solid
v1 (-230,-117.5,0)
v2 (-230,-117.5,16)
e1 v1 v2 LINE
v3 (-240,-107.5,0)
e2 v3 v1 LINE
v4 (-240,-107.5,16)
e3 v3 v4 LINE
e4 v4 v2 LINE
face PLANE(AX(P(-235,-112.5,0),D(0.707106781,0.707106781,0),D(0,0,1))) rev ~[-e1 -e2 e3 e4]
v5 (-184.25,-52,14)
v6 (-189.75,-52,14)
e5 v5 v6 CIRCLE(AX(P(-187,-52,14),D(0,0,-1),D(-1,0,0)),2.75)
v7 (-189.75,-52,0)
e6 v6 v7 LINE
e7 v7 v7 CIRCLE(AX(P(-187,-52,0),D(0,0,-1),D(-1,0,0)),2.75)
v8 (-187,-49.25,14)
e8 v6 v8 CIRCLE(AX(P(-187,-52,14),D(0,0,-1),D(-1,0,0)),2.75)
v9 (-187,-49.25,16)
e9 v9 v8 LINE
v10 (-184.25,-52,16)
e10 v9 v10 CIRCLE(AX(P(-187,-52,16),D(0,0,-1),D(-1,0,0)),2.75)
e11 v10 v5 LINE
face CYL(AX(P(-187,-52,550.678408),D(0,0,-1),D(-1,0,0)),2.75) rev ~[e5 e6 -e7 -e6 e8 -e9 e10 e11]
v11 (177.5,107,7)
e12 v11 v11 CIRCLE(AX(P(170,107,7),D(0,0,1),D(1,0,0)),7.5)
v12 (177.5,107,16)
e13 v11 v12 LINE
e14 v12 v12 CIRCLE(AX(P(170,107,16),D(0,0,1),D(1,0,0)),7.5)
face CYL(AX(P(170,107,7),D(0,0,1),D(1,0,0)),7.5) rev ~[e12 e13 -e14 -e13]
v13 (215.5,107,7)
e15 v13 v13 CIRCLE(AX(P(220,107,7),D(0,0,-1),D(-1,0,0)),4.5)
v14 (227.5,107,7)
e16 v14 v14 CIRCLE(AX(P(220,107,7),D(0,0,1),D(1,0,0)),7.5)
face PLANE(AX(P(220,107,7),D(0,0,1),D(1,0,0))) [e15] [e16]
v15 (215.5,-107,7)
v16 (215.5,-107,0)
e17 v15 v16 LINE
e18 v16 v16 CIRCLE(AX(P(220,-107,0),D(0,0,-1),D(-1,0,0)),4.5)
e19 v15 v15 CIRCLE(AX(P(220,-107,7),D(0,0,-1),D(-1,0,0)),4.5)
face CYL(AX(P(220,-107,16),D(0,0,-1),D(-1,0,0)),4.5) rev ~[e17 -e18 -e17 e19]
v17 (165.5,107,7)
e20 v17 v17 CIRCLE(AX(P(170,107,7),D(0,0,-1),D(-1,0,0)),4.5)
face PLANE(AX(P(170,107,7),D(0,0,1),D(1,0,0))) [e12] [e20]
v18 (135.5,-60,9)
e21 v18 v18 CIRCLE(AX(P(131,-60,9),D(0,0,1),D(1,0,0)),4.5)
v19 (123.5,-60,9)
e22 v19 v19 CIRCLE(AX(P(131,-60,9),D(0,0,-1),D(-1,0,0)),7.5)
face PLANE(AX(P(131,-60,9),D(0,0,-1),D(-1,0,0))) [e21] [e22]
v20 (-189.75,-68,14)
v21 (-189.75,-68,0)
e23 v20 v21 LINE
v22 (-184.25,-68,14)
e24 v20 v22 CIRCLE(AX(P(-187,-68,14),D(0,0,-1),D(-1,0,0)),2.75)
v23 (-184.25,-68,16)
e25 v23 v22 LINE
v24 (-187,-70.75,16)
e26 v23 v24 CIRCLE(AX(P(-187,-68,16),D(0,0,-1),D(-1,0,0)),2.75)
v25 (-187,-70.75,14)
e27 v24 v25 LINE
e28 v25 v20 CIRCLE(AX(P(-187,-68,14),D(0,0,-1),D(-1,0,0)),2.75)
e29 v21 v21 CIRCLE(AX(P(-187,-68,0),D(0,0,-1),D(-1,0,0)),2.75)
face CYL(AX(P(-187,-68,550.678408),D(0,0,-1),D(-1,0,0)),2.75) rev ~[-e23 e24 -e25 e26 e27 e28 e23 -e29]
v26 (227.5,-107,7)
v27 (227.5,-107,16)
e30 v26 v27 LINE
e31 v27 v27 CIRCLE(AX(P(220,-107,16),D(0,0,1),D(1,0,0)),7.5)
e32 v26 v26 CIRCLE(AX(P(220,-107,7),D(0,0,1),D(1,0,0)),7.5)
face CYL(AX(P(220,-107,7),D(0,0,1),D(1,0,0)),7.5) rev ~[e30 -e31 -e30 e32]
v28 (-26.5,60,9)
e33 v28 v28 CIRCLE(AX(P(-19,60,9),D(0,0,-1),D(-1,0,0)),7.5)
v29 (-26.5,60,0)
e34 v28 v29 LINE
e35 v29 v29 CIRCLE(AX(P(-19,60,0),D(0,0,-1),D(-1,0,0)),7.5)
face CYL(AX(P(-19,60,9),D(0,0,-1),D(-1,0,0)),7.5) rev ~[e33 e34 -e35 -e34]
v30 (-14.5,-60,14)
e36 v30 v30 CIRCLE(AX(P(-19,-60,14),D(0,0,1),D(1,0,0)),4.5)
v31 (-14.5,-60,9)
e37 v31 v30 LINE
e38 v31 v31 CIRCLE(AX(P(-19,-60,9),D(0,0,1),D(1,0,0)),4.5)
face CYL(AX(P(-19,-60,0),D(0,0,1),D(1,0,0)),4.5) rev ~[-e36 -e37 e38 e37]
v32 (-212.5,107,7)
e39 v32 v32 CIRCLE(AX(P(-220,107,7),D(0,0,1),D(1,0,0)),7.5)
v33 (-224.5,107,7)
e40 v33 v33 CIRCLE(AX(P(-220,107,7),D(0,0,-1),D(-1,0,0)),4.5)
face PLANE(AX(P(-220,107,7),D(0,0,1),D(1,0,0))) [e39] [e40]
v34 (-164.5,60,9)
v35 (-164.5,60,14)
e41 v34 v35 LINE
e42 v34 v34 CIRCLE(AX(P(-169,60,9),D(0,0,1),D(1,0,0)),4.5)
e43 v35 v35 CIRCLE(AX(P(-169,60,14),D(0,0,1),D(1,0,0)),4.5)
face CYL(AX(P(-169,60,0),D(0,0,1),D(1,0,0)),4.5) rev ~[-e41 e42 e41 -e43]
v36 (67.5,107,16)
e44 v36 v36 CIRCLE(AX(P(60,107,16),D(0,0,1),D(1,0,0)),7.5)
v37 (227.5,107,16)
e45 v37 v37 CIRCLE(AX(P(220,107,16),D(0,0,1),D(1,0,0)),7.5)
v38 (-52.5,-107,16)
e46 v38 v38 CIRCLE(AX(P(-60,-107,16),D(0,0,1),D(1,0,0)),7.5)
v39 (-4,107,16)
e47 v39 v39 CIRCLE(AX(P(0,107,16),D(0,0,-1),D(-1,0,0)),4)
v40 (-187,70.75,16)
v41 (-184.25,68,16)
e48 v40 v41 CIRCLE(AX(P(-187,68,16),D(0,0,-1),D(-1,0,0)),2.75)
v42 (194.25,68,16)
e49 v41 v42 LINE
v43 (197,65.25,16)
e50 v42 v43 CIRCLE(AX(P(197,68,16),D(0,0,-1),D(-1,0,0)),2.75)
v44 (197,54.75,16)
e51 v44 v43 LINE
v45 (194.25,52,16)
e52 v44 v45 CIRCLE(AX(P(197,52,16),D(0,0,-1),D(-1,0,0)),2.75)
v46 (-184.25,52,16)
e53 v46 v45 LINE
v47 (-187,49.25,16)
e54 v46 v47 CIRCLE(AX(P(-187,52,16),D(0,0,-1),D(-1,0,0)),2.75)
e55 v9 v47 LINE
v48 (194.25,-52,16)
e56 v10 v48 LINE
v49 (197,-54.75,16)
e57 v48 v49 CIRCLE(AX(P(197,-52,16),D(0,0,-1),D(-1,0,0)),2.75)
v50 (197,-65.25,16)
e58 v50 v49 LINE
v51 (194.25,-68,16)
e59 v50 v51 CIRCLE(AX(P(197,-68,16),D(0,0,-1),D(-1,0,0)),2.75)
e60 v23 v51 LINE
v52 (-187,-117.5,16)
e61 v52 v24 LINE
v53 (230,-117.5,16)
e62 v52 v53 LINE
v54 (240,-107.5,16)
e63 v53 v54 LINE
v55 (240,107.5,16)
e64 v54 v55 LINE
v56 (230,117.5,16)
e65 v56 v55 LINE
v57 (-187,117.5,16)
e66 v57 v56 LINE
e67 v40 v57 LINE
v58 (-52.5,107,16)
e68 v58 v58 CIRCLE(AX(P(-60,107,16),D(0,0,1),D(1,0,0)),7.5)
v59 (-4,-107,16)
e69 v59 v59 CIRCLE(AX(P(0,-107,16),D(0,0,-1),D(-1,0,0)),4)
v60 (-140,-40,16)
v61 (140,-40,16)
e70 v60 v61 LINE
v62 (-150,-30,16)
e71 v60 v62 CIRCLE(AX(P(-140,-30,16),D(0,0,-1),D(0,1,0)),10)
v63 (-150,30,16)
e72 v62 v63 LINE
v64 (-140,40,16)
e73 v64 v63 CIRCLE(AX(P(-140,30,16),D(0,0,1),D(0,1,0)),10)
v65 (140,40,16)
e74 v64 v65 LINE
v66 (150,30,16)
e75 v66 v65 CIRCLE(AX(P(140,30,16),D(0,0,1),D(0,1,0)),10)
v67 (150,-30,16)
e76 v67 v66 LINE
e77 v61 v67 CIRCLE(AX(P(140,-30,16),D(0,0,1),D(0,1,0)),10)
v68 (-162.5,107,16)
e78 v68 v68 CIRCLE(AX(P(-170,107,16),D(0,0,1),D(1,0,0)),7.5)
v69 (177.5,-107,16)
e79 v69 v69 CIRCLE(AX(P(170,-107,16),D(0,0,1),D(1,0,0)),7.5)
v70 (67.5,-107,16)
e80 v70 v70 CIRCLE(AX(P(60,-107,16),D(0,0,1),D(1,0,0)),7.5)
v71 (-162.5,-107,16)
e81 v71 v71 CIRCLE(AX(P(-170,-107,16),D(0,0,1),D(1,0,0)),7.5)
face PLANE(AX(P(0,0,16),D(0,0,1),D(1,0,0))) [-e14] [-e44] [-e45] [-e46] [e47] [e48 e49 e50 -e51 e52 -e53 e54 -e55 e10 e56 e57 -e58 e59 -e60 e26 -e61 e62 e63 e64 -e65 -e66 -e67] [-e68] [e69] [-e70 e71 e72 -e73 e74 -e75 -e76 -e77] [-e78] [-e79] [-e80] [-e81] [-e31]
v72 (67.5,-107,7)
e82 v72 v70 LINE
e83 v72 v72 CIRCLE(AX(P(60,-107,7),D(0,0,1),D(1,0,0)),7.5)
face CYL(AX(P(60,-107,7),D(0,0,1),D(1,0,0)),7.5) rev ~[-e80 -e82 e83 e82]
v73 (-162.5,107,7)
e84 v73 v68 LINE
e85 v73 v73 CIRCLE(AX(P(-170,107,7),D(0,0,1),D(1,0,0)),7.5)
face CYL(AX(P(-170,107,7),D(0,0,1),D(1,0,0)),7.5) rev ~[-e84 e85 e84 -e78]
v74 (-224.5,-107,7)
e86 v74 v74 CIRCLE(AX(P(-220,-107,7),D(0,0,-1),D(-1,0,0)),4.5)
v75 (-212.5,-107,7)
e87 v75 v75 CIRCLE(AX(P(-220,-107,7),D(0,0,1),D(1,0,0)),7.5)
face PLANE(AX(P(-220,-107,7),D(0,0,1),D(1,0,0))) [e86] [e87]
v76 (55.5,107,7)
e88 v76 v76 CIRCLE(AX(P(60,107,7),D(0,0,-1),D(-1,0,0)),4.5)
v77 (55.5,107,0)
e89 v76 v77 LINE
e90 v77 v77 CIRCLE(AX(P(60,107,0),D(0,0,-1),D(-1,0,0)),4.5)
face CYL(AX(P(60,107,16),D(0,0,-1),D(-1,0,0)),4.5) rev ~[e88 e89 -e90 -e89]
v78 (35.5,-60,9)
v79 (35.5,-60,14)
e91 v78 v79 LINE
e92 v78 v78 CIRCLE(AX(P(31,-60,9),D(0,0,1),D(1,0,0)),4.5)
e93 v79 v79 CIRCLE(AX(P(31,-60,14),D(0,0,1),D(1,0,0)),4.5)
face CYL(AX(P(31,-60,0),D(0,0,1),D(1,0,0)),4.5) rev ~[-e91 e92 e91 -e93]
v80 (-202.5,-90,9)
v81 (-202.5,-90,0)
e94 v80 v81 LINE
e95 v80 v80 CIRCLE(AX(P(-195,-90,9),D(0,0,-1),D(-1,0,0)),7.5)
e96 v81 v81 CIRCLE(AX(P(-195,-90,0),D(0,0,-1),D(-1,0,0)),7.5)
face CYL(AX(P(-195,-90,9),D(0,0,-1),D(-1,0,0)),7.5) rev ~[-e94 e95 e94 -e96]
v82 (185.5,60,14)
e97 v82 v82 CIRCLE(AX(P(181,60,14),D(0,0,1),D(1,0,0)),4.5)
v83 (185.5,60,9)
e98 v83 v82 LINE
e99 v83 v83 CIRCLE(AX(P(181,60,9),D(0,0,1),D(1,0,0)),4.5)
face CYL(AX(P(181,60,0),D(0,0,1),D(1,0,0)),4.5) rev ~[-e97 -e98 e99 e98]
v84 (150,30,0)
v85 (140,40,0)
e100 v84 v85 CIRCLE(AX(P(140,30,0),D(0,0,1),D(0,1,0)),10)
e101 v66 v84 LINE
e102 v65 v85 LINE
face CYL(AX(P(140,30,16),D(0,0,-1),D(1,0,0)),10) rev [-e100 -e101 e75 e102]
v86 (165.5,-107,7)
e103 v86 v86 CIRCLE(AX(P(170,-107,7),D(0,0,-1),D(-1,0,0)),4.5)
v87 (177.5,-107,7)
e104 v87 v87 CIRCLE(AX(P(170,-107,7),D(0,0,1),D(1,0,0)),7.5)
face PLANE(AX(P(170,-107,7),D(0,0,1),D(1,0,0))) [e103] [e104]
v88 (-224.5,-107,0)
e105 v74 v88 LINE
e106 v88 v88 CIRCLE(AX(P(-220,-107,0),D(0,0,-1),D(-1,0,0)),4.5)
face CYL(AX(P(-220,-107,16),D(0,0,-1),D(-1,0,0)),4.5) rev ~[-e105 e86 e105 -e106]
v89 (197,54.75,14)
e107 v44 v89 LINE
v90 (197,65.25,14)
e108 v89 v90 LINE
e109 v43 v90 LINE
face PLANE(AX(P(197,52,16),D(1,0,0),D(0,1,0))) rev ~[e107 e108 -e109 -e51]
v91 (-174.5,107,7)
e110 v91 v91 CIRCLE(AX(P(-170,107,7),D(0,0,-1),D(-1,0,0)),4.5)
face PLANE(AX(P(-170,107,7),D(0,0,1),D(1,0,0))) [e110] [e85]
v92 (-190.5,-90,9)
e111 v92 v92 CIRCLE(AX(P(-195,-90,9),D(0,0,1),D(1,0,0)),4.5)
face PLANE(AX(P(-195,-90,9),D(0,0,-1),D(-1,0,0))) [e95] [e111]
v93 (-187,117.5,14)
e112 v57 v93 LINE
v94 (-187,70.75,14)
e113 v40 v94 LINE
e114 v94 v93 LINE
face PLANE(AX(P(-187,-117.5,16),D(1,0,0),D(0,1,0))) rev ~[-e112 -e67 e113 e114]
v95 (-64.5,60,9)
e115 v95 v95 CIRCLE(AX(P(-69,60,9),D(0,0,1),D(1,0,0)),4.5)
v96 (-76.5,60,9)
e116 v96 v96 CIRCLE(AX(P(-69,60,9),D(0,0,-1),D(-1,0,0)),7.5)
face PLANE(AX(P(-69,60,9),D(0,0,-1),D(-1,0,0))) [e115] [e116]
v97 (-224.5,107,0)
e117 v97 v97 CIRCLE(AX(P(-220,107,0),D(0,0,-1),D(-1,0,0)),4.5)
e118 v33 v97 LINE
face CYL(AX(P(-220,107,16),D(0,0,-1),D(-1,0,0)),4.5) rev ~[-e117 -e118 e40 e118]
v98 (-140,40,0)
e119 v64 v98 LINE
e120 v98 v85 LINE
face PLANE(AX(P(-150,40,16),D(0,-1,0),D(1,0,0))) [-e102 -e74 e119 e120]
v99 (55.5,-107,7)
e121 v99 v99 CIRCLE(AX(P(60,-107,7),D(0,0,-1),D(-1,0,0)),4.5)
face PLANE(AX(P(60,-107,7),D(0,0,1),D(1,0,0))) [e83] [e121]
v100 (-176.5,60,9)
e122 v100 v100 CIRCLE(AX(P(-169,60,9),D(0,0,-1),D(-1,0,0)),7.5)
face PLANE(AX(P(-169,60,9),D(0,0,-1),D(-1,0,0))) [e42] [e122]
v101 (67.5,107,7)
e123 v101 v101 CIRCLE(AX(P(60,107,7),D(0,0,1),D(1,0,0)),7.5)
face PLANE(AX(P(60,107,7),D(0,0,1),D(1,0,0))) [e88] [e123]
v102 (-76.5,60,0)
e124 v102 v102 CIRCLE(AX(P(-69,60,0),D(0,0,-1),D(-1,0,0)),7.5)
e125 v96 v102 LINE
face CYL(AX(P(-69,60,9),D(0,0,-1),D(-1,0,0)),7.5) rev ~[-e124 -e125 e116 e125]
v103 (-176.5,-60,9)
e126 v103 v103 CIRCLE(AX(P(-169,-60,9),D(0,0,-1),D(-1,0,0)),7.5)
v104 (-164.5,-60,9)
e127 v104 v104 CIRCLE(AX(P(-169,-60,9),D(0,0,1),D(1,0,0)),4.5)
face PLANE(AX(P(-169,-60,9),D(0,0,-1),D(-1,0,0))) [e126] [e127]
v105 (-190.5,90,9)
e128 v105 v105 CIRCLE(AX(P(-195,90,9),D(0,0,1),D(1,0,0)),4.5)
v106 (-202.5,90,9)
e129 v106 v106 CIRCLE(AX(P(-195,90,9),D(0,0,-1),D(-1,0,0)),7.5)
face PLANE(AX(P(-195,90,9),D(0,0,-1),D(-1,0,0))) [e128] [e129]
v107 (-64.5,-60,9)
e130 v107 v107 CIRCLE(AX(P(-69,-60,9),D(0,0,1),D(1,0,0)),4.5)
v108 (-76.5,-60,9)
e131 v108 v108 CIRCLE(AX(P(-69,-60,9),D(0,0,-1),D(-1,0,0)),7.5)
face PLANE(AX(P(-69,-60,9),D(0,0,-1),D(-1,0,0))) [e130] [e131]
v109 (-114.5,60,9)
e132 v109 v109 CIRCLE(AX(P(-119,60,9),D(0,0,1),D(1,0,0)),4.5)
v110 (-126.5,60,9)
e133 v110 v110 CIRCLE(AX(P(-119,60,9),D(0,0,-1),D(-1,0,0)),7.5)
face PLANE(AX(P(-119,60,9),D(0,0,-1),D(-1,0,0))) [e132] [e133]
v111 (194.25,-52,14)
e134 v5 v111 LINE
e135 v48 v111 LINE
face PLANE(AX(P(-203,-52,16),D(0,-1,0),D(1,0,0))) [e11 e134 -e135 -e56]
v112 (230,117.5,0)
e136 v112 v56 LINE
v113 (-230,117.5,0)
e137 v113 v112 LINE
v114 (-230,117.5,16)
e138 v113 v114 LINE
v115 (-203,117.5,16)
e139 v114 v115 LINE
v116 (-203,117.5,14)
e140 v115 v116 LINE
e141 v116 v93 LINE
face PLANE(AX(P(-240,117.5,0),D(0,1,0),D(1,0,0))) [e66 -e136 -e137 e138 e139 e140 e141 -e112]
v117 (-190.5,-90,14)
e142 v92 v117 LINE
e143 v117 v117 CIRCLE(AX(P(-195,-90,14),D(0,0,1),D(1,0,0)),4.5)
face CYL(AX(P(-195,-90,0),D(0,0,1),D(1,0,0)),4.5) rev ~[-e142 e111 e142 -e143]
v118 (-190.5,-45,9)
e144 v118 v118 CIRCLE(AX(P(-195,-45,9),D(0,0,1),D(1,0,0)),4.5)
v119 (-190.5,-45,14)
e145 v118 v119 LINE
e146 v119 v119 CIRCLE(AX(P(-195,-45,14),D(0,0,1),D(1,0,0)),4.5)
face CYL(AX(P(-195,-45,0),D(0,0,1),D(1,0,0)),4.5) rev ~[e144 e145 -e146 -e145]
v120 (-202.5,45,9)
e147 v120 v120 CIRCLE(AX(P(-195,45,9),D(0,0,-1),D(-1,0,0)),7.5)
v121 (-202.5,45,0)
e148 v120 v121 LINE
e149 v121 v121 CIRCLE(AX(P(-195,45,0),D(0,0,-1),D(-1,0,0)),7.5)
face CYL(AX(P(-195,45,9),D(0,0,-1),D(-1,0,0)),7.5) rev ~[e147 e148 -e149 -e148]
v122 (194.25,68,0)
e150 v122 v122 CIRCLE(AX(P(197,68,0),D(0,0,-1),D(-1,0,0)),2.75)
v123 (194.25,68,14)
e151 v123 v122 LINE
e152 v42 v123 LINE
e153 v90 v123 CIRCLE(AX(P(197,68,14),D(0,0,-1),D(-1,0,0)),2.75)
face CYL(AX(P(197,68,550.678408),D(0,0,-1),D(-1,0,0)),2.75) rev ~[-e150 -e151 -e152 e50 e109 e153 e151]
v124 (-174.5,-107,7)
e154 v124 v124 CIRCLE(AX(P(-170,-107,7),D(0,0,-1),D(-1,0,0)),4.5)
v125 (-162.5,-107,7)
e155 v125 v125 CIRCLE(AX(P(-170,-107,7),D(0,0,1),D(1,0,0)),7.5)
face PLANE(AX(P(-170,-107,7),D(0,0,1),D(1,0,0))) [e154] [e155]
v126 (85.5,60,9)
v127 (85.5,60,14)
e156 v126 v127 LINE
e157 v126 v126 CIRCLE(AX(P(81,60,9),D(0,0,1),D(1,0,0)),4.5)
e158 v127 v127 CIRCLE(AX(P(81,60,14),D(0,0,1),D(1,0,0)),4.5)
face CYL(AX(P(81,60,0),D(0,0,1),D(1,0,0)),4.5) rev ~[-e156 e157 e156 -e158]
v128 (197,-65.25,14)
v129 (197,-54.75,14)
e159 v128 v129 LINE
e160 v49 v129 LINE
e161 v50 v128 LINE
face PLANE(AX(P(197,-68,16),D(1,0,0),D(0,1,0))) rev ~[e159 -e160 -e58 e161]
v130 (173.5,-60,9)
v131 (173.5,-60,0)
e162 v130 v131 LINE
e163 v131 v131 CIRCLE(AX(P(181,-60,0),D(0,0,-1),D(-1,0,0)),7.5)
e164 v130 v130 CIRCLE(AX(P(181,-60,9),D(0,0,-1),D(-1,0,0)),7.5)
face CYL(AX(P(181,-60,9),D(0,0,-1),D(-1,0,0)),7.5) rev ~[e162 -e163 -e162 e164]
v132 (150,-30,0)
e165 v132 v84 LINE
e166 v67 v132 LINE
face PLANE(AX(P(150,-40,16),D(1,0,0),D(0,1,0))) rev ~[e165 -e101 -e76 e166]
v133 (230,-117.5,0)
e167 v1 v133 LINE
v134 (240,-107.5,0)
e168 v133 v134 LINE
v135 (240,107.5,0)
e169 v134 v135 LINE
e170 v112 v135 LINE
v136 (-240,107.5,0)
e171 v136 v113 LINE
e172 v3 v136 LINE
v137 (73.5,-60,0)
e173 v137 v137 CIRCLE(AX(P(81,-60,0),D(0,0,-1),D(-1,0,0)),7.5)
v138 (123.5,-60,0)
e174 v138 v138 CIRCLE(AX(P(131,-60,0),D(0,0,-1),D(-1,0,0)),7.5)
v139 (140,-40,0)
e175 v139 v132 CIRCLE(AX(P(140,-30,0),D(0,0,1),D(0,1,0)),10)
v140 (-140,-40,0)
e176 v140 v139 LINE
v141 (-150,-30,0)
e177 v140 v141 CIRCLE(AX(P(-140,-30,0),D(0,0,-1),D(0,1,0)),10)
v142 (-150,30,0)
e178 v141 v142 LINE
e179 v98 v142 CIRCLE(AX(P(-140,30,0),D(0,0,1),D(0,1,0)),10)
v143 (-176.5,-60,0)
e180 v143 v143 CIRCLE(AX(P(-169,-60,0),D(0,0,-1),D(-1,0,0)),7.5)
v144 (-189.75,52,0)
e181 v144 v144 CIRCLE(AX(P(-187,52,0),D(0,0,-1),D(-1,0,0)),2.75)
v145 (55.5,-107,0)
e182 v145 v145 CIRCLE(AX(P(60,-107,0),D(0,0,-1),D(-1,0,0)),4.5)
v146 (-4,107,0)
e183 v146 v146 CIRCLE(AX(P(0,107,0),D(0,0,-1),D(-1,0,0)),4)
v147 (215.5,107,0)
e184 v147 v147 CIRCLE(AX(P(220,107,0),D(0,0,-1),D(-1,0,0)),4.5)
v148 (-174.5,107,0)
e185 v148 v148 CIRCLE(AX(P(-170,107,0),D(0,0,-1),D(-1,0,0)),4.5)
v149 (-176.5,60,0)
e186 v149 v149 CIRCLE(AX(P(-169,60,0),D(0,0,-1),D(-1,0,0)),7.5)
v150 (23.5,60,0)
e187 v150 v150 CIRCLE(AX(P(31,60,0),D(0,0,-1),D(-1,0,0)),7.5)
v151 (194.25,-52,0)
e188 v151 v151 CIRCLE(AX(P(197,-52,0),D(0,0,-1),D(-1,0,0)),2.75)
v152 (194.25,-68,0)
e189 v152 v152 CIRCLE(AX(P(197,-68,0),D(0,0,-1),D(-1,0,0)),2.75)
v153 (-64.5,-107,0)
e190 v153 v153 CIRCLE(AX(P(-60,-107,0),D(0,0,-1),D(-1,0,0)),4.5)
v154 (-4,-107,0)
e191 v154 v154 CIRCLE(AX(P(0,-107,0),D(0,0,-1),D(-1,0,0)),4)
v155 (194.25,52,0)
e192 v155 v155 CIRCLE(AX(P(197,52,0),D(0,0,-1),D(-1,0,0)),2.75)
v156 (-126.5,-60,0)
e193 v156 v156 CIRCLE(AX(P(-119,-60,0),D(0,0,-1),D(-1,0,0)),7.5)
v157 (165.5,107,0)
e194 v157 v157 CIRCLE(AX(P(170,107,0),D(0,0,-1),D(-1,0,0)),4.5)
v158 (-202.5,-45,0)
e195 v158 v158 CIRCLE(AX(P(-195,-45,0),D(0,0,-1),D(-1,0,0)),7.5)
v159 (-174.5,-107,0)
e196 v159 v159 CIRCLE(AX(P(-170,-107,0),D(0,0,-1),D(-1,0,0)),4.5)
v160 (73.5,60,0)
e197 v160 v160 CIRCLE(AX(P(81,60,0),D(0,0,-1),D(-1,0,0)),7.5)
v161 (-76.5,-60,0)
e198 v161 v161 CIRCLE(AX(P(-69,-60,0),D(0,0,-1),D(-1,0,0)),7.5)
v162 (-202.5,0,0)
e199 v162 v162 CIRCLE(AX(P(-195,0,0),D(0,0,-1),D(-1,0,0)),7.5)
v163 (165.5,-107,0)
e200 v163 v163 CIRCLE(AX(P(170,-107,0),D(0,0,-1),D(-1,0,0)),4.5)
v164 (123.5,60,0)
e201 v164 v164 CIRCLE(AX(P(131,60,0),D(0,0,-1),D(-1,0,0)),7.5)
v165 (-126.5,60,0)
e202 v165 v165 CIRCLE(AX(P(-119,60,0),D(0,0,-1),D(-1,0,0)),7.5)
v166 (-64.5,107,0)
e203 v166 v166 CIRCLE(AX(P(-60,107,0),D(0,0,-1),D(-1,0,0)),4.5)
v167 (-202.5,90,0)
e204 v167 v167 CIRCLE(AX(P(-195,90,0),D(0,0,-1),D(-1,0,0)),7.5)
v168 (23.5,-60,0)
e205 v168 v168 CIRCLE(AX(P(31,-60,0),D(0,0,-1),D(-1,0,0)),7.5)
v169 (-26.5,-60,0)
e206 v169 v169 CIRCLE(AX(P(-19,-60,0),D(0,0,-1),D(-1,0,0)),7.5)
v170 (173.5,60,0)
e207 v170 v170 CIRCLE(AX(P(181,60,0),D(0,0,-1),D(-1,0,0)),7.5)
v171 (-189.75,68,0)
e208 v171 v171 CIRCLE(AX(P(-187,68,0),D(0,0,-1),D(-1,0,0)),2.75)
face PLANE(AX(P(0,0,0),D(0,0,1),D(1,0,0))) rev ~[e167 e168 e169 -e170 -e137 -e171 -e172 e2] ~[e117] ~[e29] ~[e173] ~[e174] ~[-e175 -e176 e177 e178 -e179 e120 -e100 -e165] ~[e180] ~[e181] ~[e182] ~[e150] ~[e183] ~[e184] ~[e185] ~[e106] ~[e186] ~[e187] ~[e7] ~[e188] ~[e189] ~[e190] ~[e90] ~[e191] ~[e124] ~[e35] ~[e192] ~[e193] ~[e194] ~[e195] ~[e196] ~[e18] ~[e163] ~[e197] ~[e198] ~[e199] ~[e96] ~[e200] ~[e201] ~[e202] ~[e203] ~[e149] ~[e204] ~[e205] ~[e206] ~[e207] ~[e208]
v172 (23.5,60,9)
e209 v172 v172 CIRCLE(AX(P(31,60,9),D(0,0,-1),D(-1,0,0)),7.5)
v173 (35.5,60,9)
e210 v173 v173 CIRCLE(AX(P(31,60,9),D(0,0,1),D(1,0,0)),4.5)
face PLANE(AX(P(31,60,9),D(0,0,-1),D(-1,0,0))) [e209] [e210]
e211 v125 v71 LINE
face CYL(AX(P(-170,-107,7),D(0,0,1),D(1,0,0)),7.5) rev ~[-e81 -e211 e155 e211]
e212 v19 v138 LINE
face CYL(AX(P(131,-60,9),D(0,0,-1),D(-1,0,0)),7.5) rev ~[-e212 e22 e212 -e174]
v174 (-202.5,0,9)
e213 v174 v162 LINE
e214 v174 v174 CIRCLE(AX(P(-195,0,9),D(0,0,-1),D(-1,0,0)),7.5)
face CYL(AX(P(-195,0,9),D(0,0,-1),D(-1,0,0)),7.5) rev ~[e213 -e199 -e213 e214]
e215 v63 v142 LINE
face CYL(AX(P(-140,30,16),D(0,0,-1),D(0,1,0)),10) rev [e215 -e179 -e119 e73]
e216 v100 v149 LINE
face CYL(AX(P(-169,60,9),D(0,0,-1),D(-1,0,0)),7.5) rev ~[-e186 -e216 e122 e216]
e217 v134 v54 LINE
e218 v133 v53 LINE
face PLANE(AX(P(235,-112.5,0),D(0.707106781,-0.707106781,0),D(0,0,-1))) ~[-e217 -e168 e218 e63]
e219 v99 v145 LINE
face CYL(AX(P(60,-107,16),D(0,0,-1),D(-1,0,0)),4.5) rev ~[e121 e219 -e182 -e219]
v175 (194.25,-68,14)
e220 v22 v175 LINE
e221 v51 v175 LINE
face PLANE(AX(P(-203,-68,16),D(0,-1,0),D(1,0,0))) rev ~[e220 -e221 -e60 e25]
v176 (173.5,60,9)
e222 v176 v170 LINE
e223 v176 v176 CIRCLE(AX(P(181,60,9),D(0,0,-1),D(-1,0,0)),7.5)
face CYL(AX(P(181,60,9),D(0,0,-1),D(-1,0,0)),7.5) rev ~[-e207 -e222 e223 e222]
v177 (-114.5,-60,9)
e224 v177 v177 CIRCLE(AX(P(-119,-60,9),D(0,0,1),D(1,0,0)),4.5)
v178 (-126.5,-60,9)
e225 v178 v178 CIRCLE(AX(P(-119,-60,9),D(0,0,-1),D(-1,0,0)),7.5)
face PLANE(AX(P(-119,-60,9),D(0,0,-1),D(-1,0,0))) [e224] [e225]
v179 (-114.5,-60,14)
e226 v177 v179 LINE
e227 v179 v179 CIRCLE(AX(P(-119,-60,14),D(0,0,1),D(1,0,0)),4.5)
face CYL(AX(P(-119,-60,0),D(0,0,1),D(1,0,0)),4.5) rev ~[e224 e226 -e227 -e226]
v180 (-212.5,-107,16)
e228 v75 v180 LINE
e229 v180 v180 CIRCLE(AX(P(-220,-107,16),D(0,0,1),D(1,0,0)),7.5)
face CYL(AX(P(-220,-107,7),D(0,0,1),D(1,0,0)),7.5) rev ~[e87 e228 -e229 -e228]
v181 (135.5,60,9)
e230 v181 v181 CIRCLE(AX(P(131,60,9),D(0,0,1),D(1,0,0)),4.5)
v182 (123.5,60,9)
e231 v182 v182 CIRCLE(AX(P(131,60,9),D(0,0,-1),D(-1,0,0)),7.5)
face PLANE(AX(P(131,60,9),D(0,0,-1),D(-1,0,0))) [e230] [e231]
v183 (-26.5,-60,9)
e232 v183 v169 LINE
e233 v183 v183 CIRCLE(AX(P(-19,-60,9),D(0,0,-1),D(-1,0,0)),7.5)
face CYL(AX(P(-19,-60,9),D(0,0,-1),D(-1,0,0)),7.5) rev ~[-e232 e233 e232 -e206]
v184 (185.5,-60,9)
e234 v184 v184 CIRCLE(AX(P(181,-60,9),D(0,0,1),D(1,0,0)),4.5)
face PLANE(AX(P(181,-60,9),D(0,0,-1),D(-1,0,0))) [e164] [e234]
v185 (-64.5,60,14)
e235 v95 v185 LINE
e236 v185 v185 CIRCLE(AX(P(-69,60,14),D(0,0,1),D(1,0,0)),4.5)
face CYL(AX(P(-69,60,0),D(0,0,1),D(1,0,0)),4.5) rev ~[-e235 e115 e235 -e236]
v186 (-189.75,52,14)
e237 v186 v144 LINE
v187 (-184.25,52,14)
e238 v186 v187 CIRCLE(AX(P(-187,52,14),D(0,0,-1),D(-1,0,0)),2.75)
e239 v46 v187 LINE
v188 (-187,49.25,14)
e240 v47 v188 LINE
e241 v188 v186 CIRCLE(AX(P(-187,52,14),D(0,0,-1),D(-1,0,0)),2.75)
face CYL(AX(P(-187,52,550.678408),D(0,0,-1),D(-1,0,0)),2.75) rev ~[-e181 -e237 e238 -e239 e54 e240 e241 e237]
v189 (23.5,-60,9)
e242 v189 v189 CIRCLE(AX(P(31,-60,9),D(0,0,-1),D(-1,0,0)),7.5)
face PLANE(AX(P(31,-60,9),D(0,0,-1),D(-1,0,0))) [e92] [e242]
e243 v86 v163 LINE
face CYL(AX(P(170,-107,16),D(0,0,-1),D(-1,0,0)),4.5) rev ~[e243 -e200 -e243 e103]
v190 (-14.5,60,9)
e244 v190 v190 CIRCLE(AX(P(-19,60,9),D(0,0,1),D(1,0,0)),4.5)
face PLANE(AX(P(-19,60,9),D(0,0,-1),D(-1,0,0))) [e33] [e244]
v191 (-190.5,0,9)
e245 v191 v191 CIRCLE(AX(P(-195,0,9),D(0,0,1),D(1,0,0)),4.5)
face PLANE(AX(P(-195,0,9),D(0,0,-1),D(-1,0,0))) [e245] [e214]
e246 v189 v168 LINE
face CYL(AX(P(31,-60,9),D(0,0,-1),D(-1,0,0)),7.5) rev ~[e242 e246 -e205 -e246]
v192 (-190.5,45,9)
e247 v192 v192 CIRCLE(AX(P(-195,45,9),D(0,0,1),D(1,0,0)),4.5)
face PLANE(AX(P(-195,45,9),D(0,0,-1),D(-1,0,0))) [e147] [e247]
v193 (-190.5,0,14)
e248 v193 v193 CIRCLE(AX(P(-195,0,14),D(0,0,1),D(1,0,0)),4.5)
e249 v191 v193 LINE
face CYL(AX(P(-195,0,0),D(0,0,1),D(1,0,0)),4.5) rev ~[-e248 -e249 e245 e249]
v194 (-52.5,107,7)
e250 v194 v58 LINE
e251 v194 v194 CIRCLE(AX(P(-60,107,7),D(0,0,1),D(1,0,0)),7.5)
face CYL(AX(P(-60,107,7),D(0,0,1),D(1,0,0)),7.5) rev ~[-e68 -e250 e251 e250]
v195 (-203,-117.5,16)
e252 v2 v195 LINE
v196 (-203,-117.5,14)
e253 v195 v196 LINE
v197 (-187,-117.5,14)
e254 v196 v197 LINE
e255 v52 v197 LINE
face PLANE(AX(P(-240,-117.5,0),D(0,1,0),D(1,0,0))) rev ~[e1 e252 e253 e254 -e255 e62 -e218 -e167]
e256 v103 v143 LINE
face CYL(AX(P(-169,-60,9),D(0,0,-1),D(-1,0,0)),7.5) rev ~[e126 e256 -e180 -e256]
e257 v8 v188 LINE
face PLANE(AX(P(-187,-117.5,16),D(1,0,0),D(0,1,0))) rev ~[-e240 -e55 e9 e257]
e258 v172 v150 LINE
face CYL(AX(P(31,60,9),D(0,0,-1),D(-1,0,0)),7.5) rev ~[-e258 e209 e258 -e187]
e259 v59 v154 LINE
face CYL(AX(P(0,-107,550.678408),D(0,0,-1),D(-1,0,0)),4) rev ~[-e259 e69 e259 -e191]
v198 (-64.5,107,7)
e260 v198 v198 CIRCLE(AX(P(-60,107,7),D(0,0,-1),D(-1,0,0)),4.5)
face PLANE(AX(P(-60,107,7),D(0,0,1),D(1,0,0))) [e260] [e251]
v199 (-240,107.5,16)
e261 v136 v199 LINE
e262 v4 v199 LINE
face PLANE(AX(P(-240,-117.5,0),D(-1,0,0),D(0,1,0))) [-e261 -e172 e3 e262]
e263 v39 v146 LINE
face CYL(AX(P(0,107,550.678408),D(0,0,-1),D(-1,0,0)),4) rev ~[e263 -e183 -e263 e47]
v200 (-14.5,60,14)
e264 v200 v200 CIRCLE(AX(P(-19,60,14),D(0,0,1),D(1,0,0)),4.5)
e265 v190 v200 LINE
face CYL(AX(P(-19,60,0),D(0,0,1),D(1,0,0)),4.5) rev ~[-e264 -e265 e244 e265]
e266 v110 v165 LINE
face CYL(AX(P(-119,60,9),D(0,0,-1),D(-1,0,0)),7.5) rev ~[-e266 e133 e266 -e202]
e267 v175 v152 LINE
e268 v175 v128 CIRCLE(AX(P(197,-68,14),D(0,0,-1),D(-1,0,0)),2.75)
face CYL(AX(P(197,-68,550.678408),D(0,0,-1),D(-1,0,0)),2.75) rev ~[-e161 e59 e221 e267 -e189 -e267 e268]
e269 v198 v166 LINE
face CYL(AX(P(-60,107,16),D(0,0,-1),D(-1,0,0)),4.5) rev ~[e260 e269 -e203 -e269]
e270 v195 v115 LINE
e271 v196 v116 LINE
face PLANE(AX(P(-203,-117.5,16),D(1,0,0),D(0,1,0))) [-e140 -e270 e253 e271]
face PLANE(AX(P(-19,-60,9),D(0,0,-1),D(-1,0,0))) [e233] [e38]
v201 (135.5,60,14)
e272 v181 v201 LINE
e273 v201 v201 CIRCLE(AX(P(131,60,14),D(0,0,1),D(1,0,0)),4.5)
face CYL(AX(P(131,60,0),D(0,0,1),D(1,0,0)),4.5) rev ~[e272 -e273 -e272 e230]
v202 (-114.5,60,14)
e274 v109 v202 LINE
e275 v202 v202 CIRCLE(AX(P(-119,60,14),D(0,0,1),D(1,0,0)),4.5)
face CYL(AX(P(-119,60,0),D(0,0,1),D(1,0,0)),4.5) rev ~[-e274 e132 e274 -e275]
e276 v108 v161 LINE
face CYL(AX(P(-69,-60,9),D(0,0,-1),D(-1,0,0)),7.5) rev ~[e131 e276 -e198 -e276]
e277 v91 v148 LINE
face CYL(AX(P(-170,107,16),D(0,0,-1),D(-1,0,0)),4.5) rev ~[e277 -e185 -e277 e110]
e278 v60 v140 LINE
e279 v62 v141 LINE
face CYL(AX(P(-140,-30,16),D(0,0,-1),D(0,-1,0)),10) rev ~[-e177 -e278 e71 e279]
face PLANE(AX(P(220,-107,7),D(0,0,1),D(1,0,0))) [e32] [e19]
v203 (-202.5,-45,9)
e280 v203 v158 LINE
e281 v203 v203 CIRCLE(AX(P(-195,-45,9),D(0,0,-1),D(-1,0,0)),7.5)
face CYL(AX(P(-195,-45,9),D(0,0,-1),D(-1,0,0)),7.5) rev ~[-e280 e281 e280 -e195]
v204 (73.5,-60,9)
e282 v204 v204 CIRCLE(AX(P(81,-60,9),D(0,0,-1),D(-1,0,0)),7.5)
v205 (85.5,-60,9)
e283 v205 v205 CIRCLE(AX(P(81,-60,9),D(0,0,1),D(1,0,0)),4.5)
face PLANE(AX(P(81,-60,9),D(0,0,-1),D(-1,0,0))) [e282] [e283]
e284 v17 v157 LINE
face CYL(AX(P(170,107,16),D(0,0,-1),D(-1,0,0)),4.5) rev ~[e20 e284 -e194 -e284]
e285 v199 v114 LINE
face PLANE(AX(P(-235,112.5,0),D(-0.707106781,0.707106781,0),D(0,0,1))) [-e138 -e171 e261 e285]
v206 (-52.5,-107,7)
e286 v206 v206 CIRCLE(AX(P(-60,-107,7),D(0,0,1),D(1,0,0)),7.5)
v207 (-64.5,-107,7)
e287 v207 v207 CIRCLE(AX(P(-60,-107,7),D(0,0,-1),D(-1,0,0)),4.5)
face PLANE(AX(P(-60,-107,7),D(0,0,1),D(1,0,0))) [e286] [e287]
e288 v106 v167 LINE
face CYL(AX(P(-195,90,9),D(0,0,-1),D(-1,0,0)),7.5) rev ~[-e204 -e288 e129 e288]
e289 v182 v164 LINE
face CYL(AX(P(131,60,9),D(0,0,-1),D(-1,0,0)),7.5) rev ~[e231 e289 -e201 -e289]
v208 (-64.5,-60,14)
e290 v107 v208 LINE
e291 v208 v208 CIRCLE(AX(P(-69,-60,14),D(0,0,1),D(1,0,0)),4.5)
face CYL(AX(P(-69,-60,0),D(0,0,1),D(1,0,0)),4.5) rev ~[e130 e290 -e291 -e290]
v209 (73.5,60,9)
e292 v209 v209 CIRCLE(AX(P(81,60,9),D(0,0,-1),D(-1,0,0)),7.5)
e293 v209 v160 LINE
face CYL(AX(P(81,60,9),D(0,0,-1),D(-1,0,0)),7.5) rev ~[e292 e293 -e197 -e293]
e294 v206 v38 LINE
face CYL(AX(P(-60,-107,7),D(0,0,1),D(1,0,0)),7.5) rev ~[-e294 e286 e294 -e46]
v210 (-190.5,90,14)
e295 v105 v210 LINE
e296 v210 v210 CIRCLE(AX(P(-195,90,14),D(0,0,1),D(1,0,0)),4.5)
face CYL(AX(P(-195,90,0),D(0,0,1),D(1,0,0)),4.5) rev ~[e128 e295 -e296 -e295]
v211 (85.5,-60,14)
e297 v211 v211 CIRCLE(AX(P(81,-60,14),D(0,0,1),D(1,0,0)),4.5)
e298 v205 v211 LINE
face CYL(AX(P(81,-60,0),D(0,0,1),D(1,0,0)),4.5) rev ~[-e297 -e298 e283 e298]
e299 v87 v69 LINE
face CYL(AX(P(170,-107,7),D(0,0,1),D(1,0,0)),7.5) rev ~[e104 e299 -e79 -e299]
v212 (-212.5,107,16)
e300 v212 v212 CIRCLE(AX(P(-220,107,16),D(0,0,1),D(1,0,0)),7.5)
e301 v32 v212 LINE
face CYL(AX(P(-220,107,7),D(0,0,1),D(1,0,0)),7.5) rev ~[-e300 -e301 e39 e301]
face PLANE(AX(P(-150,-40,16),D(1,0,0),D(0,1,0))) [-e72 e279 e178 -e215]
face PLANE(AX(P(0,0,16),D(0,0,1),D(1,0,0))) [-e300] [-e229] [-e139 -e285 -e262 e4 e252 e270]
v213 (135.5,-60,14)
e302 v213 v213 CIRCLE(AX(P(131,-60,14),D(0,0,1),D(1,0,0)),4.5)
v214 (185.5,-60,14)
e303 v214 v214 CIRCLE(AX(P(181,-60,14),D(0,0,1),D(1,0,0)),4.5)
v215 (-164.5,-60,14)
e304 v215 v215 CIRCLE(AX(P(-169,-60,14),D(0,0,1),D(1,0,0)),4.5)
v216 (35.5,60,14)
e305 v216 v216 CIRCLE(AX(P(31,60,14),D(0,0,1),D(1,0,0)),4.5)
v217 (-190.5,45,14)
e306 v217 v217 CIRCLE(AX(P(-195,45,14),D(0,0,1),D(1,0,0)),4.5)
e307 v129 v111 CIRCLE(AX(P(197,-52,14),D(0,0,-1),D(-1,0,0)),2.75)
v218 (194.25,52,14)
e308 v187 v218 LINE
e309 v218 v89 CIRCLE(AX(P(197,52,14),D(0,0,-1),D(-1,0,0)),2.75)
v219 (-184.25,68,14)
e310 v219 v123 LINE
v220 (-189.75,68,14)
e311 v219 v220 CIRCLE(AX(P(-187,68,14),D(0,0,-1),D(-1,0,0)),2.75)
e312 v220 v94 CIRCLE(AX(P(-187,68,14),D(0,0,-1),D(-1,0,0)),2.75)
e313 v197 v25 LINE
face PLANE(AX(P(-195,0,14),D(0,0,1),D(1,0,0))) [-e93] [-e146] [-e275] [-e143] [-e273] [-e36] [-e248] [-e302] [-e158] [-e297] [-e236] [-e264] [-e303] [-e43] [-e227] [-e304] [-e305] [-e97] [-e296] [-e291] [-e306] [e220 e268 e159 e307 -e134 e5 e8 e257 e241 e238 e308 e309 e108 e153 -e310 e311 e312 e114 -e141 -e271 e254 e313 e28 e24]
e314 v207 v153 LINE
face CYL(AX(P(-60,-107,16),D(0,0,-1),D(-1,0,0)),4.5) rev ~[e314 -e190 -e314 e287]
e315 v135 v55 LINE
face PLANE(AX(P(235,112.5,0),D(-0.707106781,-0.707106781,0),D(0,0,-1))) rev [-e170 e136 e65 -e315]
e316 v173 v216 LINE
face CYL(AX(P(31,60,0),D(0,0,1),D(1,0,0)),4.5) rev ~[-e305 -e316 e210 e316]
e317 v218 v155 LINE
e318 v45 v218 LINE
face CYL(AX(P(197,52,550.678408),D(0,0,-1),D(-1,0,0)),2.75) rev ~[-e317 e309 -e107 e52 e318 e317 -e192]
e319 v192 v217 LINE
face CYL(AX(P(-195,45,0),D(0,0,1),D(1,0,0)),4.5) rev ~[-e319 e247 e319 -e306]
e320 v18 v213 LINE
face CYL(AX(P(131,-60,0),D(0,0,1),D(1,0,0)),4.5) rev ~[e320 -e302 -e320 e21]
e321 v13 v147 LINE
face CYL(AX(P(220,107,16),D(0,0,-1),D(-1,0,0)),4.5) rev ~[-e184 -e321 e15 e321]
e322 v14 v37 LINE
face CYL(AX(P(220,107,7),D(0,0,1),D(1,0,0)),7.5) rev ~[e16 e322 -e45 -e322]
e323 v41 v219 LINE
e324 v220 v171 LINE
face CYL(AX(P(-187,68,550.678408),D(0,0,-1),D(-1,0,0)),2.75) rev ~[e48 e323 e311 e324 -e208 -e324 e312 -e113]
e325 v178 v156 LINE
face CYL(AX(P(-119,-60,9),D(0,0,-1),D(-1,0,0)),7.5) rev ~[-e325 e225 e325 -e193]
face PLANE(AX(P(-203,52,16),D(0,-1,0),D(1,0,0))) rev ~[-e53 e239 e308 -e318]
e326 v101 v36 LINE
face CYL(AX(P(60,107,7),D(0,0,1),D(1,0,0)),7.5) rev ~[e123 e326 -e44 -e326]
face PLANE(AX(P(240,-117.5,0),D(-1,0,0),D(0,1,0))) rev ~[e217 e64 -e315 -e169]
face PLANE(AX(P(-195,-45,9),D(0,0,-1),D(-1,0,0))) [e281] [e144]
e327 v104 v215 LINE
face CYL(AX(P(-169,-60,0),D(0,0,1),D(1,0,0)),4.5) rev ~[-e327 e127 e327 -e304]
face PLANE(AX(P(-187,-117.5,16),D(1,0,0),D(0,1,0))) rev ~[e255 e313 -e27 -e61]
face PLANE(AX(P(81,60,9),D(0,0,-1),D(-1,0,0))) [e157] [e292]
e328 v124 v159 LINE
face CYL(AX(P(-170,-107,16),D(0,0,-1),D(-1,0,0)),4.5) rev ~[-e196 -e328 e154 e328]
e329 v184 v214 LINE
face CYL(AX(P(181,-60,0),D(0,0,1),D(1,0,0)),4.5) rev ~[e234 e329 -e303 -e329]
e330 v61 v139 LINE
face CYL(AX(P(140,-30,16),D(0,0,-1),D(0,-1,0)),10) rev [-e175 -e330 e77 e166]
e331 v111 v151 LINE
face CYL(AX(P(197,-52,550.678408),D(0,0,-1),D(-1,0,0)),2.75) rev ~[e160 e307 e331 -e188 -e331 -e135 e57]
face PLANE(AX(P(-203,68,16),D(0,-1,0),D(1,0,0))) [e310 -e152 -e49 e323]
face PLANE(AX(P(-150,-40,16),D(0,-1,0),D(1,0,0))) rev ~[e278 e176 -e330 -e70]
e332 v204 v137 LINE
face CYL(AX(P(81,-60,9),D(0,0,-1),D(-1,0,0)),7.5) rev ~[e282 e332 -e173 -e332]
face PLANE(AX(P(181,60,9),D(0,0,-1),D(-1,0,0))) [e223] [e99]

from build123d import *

# Parameters (mm, degrees)
SKETCH_1_W                  = 480
SKETCH_1_H                  = 235
EXTRUDE_1_DEPTH             = 16
HOLE_WIZARD_1_D             = 9
HOLE_WIZARD_1_CBORE_D       = 15
HOLE_WIZARD_1_CBORE_DEPTH   = 9
CHAMFER_1_SIZE              = 10
MM_1_D                      = 8
SKETCH_16_W                 = 16
SKETCH_16_H                 = 235
CUT_EXTRUDE_1_DEPTH         = 2
SKETCH_17_W                 = 400
SKETCH_17_H                 = 16
CUT_EXTRUDE_2_DEPTH         = 2
SKETCH_18_W                 = 300
SKETCH_18_H                 = 80
CUT_EXTRUDE_3_DEPTH         = 268.69805752
FILLET_1_R                  = 10
HOLE_WIZARD_3_D             = 9
HOLE_WIZARD_3_CBORE_D       = 15
HOLE_WIZARD_3_CBORE_DEPTH   = 9
HOLE_WIZARD_3_2_D           = 9
HOLE_WIZARD_3_2_CBORE_D     = 15
HOLE_WIZARD_3_2_CBORE_DEPTH = 9
PATTERN_LINEAR_1_COUNT      = 8
PATTERN_LINEAR_1_PITCH      = 50
HOLE_WIZARD_5_5_5_5_1_D     = 5.5


with BuildPart() as part:
    # 草图1 → 凸台-拉伸1 (new body)
    with BuildSketch(Plane.XY):
        Rectangle(SKETCH_1_W, SKETCH_1_H)
    extrude(amount=EXTRUDE_1_DEPTH)

    # 打孔尺寸(%根据)内六角圆柱头螺钉的类型1 (through all)
    with Locations(Plane.XY.offset(16)):
        with Locations((-220, 107), (220, -107), (-220, -107), (220, 107), (-170, 107), (-170, -107), (-60, 107), (-60, -107), (60, 107), (60, -107), (170, 107), (170, -107)):
            CounterBoreHole(HOLE_WIZARD_1_D / 2, HOLE_WIZARD_1_CBORE_D / 2, HOLE_WIZARD_1_CBORE_DEPTH)

    # 倒角1
    chamfer_1_edges = [part.edges().sort_by_distance(p)[0] for p in [
        (-240, 117.5, 8),
        (240, 117.5, 8),
        (240, -117.5, 8),
        (-240, -117.5, 8),
    ]]
    chamfer(chamfer_1_edges, length=CHAMFER_1_SIZE)

    # 大小mm 暗销孔1 (through all)
    with Locations(Plane.XY.offset(16)):
        with Locations((0, -107), (0, 107)):
            Hole(MM_1_D / 2)

    # 草图16 → 切除-拉伸1 (cut)
    with BuildSketch(Plane.XY.offset(16)):
        with Locations((-195, 0)):
            Rectangle(SKETCH_16_W, SKETCH_16_H)
    extrude(amount=-CUT_EXTRUDE_1_DEPTH, mode=Mode.SUBTRACT)

    # 草图17 → 切除-拉伸2 (cut)
    with BuildSketch(Plane.XY.offset(16)):
        with Locations((-3, -60)):
            Rectangle(SKETCH_17_W, SKETCH_17_H)
        with Locations((-3, 60)):
            Rectangle(SKETCH_17_W, SKETCH_17_H)
    extrude(amount=-CUT_EXTRUDE_2_DEPTH, mode=Mode.SUBTRACT)

    # 草图18 → 切除-拉伸3 (cut, through all)
    with BuildSketch(Plane.XY.offset(16)):
        Rectangle(SKETCH_18_W, SKETCH_18_H)
    extrude(amount=-CUT_EXTRUDE_3_DEPTH, mode=Mode.SUBTRACT)

    # 圆角1
    fillet_1_edges = [part.edges().sort_by_distance(p)[0] for p in [
        (150, 40, 8),
        (150, -40, 8),
        (-150, -40, 8),
        (-150, 40, 8),
    ]]
    fillet(fillet_1_edges, radius=FILLET_1_R)

    # Hole Wizard 3 (through all)
    with Locations(Plane(origin=(0, 0, 0), x_dir=(-1, 0, 0), z_dir=(0, 0, -1))):
        with Locations((195, 0), (195, 45), (195, 90), (195, -90), (195, -45)):
            CounterBoreHole(HOLE_WIZARD_3_D / 2, HOLE_WIZARD_3_CBORE_D / 2, HOLE_WIZARD_3_CBORE_DEPTH)

    # Hole Wizard 3 2 (through all)
    with Locations(Plane(origin=(0, 0, 0), x_dir=(-1, 0, 0), z_dir=(0, 0, -1))):
        with Locations((169, -60), (169, 60)):
            hole_wizard_3_2 = CounterBoreHole(HOLE_WIZARD_3_2_D / 2, HOLE_WIZARD_3_2_CBORE_D / 2, HOLE_WIZARD_3_2_CBORE_DEPTH)

    # 阵列(线性)1: Hole Wizard 3 2 ×8
    with Locations(*[(i * PATTERN_LINEAR_1_PITCH, 0, 0) for i in range(1, PATTERN_LINEAR_1_COUNT)]):
        add(hole_wizard_3_2, mode=Mode.SUBTRACT)

    # Ø5.5 (5.5) 直径孔1 (through all)
    with Locations(Plane.XY.offset(16)):
        with Locations((197, -68), (197, -52), (197, 52), (197, 68), (-187, 68), (-187, 52), (-187, -68), (-187, -52)):
            Hole(HOLE_WIZARD_5_5_5_5_1_D / 2)


solid = part.part
